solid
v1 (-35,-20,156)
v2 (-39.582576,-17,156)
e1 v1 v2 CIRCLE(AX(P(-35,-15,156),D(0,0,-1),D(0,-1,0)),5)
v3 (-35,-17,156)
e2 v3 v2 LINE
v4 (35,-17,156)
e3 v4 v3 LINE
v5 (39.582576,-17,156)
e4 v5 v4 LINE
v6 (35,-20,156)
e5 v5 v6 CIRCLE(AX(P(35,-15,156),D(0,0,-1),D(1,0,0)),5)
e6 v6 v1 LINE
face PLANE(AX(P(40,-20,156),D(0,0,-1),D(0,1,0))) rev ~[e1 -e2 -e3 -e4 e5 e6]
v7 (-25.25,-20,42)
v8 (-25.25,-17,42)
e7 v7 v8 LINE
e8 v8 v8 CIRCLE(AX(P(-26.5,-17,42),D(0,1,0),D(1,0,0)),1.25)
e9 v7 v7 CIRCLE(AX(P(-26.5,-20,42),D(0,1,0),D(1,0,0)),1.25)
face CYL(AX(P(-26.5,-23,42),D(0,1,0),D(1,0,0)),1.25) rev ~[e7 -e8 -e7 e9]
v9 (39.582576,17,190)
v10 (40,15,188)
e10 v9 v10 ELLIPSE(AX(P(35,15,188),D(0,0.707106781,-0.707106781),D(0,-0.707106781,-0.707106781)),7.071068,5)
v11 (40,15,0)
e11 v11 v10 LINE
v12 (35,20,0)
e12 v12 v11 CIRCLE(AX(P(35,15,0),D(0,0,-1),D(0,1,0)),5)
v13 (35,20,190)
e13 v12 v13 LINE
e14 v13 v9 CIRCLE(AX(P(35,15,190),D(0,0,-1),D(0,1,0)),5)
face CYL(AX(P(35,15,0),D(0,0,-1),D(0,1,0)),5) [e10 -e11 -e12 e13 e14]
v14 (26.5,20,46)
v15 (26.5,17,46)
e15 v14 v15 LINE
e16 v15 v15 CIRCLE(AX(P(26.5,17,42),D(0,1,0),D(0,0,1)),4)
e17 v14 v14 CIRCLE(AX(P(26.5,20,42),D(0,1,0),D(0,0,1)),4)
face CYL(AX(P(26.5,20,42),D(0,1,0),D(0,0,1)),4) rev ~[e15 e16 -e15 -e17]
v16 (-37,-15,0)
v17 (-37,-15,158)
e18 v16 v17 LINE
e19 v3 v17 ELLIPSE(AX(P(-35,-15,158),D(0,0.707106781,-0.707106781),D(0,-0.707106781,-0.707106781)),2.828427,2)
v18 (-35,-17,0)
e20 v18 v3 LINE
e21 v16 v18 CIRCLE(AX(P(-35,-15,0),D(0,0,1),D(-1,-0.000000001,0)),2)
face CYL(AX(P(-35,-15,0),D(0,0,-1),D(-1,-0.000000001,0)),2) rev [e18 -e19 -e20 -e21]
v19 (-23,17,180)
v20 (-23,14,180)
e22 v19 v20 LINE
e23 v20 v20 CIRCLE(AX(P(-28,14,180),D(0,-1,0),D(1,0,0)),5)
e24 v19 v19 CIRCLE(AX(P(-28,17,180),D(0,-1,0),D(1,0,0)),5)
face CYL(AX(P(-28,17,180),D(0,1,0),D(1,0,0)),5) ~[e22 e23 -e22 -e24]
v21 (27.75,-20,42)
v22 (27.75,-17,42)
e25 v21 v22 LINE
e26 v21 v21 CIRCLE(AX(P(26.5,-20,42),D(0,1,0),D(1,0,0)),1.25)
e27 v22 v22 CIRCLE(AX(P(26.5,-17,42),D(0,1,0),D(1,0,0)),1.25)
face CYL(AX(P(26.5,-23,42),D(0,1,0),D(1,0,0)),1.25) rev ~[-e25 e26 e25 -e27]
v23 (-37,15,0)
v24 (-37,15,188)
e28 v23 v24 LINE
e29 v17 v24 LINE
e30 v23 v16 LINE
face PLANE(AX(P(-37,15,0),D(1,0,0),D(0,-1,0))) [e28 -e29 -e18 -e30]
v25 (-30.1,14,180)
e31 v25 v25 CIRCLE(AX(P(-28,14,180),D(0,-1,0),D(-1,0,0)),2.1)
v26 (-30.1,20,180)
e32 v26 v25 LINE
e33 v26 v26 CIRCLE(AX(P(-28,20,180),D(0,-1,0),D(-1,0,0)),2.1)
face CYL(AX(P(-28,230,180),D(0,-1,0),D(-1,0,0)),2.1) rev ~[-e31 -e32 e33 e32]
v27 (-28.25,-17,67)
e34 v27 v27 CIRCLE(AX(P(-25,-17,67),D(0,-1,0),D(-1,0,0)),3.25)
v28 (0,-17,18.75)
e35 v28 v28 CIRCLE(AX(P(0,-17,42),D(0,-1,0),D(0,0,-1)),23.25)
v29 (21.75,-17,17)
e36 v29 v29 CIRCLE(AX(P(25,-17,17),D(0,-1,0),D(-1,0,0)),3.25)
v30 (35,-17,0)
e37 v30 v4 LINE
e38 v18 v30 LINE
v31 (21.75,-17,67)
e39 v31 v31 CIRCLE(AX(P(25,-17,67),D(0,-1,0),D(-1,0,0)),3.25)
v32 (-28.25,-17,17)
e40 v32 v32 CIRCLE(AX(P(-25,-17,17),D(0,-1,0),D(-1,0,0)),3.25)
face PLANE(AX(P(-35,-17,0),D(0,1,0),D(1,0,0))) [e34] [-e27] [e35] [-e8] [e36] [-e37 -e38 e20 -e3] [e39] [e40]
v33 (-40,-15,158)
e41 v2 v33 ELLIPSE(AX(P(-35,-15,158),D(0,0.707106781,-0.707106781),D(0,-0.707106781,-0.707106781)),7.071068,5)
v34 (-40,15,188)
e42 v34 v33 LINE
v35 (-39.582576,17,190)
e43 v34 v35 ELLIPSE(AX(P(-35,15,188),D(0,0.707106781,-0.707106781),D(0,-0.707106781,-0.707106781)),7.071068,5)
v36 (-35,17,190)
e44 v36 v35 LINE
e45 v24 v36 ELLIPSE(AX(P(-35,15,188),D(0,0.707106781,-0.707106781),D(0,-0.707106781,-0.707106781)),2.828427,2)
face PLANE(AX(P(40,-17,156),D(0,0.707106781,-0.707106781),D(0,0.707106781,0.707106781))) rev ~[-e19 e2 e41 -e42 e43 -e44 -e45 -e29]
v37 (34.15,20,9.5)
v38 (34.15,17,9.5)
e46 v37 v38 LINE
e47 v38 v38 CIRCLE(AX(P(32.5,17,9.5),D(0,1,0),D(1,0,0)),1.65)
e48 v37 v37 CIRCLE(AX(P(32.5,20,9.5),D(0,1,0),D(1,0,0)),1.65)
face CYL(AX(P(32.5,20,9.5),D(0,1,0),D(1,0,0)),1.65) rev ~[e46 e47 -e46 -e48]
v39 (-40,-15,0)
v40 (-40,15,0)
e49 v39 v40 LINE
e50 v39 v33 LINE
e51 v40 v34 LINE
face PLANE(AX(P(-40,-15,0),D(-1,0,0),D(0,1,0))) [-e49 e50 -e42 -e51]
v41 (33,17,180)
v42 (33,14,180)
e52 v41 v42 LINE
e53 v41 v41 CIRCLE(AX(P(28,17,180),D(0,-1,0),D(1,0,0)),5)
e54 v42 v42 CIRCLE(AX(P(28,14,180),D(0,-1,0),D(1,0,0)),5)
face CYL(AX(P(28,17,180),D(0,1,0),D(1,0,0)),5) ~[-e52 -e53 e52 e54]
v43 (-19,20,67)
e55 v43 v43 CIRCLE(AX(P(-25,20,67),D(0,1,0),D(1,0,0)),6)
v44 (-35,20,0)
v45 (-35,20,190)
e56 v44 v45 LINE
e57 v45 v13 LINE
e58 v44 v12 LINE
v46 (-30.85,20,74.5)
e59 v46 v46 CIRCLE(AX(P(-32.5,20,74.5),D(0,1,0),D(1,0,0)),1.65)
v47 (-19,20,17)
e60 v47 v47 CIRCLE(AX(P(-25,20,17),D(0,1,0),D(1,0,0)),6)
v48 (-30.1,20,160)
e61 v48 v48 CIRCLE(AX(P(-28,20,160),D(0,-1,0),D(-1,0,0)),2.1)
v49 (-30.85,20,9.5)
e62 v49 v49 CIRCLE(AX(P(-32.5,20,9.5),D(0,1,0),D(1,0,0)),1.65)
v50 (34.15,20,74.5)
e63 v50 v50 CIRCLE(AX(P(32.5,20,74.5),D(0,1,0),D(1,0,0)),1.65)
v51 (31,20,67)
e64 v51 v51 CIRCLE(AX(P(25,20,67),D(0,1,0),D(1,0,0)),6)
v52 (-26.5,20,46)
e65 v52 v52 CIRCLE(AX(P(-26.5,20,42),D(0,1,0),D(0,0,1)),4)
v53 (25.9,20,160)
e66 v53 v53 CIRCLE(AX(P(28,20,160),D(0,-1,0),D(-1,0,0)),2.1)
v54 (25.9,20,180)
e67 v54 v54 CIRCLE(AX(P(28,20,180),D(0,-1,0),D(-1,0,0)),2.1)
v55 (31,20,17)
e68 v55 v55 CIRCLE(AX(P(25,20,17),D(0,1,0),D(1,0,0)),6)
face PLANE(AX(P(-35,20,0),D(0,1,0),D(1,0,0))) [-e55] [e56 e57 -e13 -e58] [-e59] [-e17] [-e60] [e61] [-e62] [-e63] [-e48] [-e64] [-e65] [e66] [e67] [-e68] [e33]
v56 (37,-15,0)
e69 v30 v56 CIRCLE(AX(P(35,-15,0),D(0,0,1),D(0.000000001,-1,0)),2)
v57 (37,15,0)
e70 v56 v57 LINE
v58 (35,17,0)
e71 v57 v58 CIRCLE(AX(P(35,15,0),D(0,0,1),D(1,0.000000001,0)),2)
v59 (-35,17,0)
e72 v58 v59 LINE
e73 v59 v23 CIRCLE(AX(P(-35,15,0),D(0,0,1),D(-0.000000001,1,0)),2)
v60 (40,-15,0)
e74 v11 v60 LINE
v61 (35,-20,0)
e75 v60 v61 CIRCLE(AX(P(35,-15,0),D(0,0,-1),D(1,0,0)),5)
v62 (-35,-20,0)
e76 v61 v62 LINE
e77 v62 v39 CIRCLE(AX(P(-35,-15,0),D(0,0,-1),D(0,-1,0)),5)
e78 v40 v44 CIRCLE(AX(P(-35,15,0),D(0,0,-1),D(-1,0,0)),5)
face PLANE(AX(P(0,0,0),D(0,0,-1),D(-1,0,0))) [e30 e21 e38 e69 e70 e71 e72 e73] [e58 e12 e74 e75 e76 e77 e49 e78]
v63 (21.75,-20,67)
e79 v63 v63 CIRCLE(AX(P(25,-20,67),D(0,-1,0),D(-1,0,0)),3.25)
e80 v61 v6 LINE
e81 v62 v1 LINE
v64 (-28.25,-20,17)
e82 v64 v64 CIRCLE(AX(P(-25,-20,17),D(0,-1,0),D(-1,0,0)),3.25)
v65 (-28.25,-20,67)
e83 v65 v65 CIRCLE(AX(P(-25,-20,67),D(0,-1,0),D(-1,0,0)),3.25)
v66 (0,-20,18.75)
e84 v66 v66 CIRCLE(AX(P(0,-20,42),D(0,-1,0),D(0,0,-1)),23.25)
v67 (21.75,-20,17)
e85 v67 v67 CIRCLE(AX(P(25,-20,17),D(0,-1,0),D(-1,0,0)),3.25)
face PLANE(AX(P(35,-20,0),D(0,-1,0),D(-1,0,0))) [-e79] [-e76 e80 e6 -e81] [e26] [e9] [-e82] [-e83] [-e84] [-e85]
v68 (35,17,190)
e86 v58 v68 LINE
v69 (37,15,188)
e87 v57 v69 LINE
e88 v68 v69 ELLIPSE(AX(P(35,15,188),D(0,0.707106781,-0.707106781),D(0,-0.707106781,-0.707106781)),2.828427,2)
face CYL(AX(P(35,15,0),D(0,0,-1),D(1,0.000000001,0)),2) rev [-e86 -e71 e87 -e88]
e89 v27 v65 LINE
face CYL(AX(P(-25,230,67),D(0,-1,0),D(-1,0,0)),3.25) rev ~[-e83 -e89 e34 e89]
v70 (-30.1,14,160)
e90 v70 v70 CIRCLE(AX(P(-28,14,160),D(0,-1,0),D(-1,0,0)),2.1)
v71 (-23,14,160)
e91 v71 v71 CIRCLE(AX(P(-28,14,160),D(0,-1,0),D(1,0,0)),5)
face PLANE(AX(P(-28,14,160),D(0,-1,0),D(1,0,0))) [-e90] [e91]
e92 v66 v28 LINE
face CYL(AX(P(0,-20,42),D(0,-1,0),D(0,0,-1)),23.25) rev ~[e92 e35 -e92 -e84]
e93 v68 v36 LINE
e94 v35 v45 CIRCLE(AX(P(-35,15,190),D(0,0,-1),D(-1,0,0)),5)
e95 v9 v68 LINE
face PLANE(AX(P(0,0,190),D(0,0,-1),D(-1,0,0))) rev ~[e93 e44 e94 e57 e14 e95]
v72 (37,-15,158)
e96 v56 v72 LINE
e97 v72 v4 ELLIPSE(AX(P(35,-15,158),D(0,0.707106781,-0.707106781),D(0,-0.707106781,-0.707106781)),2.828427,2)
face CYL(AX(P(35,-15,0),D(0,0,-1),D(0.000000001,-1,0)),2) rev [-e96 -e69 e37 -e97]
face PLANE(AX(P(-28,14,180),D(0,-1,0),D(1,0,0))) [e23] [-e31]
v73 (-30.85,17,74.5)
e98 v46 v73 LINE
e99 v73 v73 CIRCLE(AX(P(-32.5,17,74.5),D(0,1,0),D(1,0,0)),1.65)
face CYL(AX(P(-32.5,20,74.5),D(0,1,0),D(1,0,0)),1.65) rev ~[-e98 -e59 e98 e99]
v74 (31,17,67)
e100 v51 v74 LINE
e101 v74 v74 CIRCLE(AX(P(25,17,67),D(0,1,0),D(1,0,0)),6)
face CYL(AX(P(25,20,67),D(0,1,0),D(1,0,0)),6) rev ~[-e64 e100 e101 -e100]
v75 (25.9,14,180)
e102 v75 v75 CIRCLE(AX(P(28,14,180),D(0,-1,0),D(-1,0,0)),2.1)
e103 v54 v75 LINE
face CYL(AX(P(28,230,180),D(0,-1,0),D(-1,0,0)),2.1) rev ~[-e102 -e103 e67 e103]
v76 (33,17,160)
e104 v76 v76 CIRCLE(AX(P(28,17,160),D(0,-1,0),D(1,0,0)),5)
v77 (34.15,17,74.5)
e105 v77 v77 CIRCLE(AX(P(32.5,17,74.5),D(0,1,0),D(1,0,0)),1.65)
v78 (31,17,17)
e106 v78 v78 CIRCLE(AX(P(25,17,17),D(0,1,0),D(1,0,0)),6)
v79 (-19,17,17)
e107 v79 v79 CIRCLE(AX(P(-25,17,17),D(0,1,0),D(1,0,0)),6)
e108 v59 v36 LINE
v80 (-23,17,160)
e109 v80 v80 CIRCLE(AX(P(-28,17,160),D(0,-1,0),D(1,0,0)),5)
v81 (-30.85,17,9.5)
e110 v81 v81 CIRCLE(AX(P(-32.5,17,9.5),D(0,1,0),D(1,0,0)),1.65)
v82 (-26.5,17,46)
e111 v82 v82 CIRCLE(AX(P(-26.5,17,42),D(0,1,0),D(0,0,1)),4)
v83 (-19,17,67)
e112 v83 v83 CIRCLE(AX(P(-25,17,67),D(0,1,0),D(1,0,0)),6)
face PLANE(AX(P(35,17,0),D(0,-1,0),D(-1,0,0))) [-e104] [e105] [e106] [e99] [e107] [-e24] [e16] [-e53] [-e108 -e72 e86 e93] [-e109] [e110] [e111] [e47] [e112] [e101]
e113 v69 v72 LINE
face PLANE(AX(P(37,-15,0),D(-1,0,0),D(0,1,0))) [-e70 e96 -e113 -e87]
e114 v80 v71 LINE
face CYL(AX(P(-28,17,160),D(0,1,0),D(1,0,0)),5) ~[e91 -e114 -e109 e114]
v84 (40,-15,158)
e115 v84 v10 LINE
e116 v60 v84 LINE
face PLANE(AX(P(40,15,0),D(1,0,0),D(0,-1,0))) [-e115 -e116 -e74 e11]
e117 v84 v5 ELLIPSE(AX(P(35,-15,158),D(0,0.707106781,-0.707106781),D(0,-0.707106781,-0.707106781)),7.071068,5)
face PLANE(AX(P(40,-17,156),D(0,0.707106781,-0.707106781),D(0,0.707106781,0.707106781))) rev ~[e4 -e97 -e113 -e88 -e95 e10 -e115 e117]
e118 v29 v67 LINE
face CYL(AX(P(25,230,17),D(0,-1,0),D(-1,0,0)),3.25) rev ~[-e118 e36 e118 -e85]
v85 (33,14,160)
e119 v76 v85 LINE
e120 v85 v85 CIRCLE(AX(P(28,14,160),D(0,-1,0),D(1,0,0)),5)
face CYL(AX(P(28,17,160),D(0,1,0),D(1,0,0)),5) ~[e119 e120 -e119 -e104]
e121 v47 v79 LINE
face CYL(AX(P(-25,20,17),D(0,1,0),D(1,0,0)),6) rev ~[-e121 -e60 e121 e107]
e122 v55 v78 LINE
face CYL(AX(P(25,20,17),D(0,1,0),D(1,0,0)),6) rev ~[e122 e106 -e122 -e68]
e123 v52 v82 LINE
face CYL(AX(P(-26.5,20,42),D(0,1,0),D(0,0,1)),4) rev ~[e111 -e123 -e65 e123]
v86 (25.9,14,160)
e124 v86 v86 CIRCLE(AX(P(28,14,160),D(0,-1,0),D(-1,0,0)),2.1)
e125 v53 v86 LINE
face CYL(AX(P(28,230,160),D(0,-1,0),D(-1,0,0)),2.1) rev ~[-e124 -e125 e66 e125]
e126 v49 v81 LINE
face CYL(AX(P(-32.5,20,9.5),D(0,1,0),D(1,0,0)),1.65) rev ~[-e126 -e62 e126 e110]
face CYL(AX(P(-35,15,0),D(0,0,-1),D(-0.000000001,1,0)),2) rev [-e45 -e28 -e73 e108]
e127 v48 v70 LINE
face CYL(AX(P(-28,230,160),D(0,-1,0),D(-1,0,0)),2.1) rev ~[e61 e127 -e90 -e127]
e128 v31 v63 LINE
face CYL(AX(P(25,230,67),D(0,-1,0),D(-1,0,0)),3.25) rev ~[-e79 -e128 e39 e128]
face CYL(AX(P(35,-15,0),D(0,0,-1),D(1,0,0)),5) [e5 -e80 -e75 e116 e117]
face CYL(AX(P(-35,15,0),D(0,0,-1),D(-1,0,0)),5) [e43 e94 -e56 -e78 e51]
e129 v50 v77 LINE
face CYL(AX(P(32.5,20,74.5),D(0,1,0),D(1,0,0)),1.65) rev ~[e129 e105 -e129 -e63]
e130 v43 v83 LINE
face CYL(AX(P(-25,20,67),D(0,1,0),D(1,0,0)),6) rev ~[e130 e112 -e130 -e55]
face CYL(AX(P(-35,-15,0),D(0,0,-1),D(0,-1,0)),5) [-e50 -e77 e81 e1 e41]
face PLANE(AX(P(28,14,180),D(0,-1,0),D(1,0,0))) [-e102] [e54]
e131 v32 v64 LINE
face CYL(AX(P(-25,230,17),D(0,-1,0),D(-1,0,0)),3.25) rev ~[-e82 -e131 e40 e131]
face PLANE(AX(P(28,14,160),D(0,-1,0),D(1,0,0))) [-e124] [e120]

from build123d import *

# Parameters (mm, degrees)
EXTRUDE_1_DEPTH              = 190
SKETCH_6_R                   = 23.25
CUT_EXTRUDE_1_DEPTH          = 3
HOLE_WIZARD_6_5_6_5_1_D      = 6.5
HOLE_WIZARD_12_0_12_1_REACH  = 200.242
HOLE_WIZARD_12_0_12_1_BORE_R = 6
HOLE_WIZARD_M4_1_REACH       = 200.242
HOLE_WIZARD_M4_1_BORE_R      = 1.65
CUT_EXTRUDE_2_DEPTH          = 208.123151772
SKETCH_12_R                  = 5
EXTRUDE_2_DEPTH              = 3
HOLE_WIZARD_M5_1_D           = 4.2
HOLE_WIZARD_M3_1_D           = 2.5
HOLE_WIZARD_M3_1_DEPTH       = 3
CUT_EXTRUDE_3_REACH          = 200.242
SKETCH_17_R                  = 4


with BuildPart() as part:
    # 草图1 → 凸台-拉伸1 (new body)
    with BuildSketch(Plane.XY):
        with BuildLine():
            Line((-35, 20), (35, 20))
            ThreePointArc((35, 20), (38.535533906, 18.535533906), (40, 15))
            Line((40, 15), (40, -15))
            ThreePointArc((40, -15), (38.535533906, -18.535533906), (35, -20))
            Line((35, -20), (-35, -20))
            ThreePointArc((-35, -20), (-38.535533906, -18.535533906), (-40, -15))
            Line((-40, -15), (-40, 15))
            ThreePointArc((-40, 15), (-38.535533906, 18.535533906), (-35, 20))
        make_face()
        with BuildLine():
            Line((-37, 15), (-37, -15))
            ThreePointArc((-37, -15), (-36.414213562, -16.414213562), (-35, -17))
            Line((-35, -17), (35, -17))
            ThreePointArc((35, -17), (36.414213562, -16.414213562), (37, -15))
            Line((37, -15), (37, 15))
            ThreePointArc((37, 15), (36.414213562, 16.414213562), (35, 17))
            Line((35, 17), (-35, 17))
            ThreePointArc((-35, 17), (-36.414213562, 16.414213562), (-37, 15))
        make_face(mode=Mode.SUBTRACT)
    extrude(amount=EXTRUDE_1_DEPTH)

    # 草图6 → 切除-拉伸1 (cut)
    with BuildSketch(Plane.XZ.offset(20)):
        with Locations(Location((0, 42, 0), (0, 0, 270))):
            Circle(SKETCH_6_R)
    extrude(amount=-CUT_EXTRUDE_1_DEPTH, mode=Mode.SUBTRACT)

    # Ø6.5 (6.5) 直径孔1 (through all)
    with Locations(Plane(origin=(0, 20, 0), x_dir=(1, 0, 0), z_dir=(0, 1, 0))):
        with Locations((-25, -17), (25, -17), (25, -67), (-25, -67)):
            Hole(HOLE_WIZARD_6_5_6_5_1_D / 2)

    # Ø12.0 (12) 直径孔1 bore → Ø12.0 (12) 直径孔1 (cut, up to next)
    with BuildSketch(Plane(origin=(0, 20, 0), x_dir=(1, 0, 0), z_dir=(0, 1, 0)), mode=Mode.PRIVATE) as hole_wizard_12_0_12_1_sk1:
        with Locations((-25, -17)):
            Circle(HOLE_WIZARD_12_0_12_1_BORE_R)
    hole_wizard_12_0_12_1_tool1 = extrude(hole_wizard_12_0_12_1_sk1.sketch, amount=-HOLE_WIZARD_12_0_12_1_REACH, mode=Mode.PRIVATE) & part.part
    # Ø12.0 (12) 直径孔1 bore → Ø12.0 (12) 直径孔1 (cut, up to next)
    with BuildSketch(Plane(origin=(0, 20, 0), x_dir=(1, 0, 0), z_dir=(0, 1, 0)), mode=Mode.PRIVATE) as hole_wizard_12_0_12_1_sk2:
        with Locations((25, -17)):
            Circle(HOLE_WIZARD_12_0_12_1_BORE_R)
    hole_wizard_12_0_12_1_tool2 = extrude(hole_wizard_12_0_12_1_sk2.sketch, amount=-HOLE_WIZARD_12_0_12_1_REACH, mode=Mode.PRIVATE) & part.part
    # Ø12.0 (12) 直径孔1 bore → Ø12.0 (12) 直径孔1 (cut, up to next)
    with BuildSketch(Plane(origin=(0, 20, 0), x_dir=(1, 0, 0), z_dir=(0, 1, 0)), mode=Mode.PRIVATE) as hole_wizard_12_0_12_1_sk3:
        with Locations((25, -67)):
            Circle(HOLE_WIZARD_12_0_12_1_BORE_R)
    hole_wizard_12_0_12_1_tool3 = extrude(hole_wizard_12_0_12_1_sk3.sketch, amount=-HOLE_WIZARD_12_0_12_1_REACH, mode=Mode.PRIVATE) & part.part
    # Ø12.0 (12) 直径孔1 bore → Ø12.0 (12) 直径孔1 (cut, up to next)
    with BuildSketch(Plane(origin=(0, 20, 0), x_dir=(1, 0, 0), z_dir=(0, 1, 0)), mode=Mode.PRIVATE) as hole_wizard_12_0_12_1_sk4:
        with Locations((-25, -67)):
            Circle(HOLE_WIZARD_12_0_12_1_BORE_R)
    hole_wizard_12_0_12_1_tool4 = extrude(hole_wizard_12_0_12_1_sk4.sketch, amount=-HOLE_WIZARD_12_0_12_1_REACH, mode=Mode.PRIVATE) & part.part
    add(hole_wizard_12_0_12_1_tool1.solids().sort_by_distance((-25, 20, 17))[0], mode=Mode.SUBTRACT)
    add(hole_wizard_12_0_12_1_tool2.solids().sort_by_distance((25, 20, 17))[0], mode=Mode.SUBTRACT)
    add(hole_wizard_12_0_12_1_tool3.solids().sort_by_distance((25, 20, 67))[0], mode=Mode.SUBTRACT)
    add(hole_wizard_12_0_12_1_tool4.solids().sort_by_distance((-25, 20, 67))[0], mode=Mode.SUBTRACT)

    # M4 螺纹孔1 bore → M4 螺纹孔1 (cut, up to next)
    with BuildSketch(Plane(origin=(0, 20, 0), x_dir=(1, 0, 0), z_dir=(0, 1, 0)), mode=Mode.PRIVATE) as hole_wizard_m4_1_sk1:
        with Locations((-32.5, -9.5)):
            Circle(HOLE_WIZARD_M4_1_BORE_R)
    hole_wizard_m4_1_tool1 = extrude(hole_wizard_m4_1_sk1.sketch, amount=-HOLE_WIZARD_M4_1_REACH, mode=Mode.PRIVATE) & part.part
    # M4 螺纹孔1 bore → M4 螺纹孔1 (cut, up to next)
    with BuildSketch(Plane(origin=(0, 20, 0), x_dir=(1, 0, 0), z_dir=(0, 1, 0)), mode=Mode.PRIVATE) as hole_wizard_m4_1_sk2:
        with Locations((32.5, -9.5)):
            Circle(HOLE_WIZARD_M4_1_BORE_R)
    hole_wizard_m4_1_tool2 = extrude(hole_wizard_m4_1_sk2.sketch, amount=-HOLE_WIZARD_M4_1_REACH, mode=Mode.PRIVATE) & part.part
    # M4 螺纹孔1 bore → M4 螺纹孔1 (cut, up to next)
    with BuildSketch(Plane(origin=(0, 20, 0), x_dir=(1, 0, 0), z_dir=(0, 1, 0)), mode=Mode.PRIVATE) as hole_wizard_m4_1_sk3:
        with Locations((32.5, -74.5)):
            Circle(HOLE_WIZARD_M4_1_BORE_R)
    hole_wizard_m4_1_tool3 = extrude(hole_wizard_m4_1_sk3.sketch, amount=-HOLE_WIZARD_M4_1_REACH, mode=Mode.PRIVATE) & part.part
    # M4 螺纹孔1 bore → M4 螺纹孔1 (cut, up to next)
    with BuildSketch(Plane(origin=(0, 20, 0), x_dir=(1, 0, 0), z_dir=(0, 1, 0)), mode=Mode.PRIVATE) as hole_wizard_m4_1_sk4:
        with Locations((-32.5, -74.5)):
            Circle(HOLE_WIZARD_M4_1_BORE_R)
    hole_wizard_m4_1_tool4 = extrude(hole_wizard_m4_1_sk4.sketch, amount=-HOLE_WIZARD_M4_1_REACH, mode=Mode.PRIVATE) & part.part
    add(hole_wizard_m4_1_tool1.solids().sort_by_distance((-32.5, 20, 9.5))[0], mode=Mode.SUBTRACT)
    add(hole_wizard_m4_1_tool2.solids().sort_by_distance((32.5, 20, 9.5))[0], mode=Mode.SUBTRACT)
    add(hole_wizard_m4_1_tool3.solids().sort_by_distance((32.5, 20, 74.5))[0], mode=Mode.SUBTRACT)
    add(hole_wizard_m4_1_tool4.solids().sort_by_distance((-32.5, 20, 74.5))[0], mode=Mode.SUBTRACT)

    # 草图9 → 切除-拉伸2 (cut, through all)
    with BuildSketch(Plane(origin=(40, 0, 0), x_dir=(0, 0, -1), z_dir=(1, 0, 0))):
        Polygon((-190, 17), (-190, -20), (-156, -20), (-156, -17), align=None)
    extrude(amount=-CUT_EXTRUDE_2_DEPTH, mode=Mode.SUBTRACT)

    # 草图12 → 凸台-拉伸2 (add)
    with BuildSketch(Plane.XZ.offset(-17)):
        with Locations((-28, 160)):
            Circle(SKETCH_12_R)
        with Locations((-28, 180)):
            Circle(SKETCH_12_R)
        with Locations((28, 160)):
            Circle(SKETCH_12_R)
        with Locations((28, 180)):
            Circle(SKETCH_12_R)
    extrude(amount=EXTRUDE_2_DEPTH)

    # M5 螺纹孔1 (through all)
    with Locations(Plane(origin=(0, 20, 0), x_dir=(1, 0, 0), z_dir=(0, 1, 0))):
        with Locations((-28, -160), (-28, -180), (28, -160), (28, -180)):
            Hole(HOLE_WIZARD_M5_1_D / 2)

    # M3 螺纹孔1
    with Locations(Plane(origin=(0, -20, 0), x_dir=(-1, 0, 0), z_dir=(0, -1, 0))):
        with Locations((26.5, -42), (-26.5, -42)):
            Hole(HOLE_WIZARD_M3_1_D / 2, depth=HOLE_WIZARD_M3_1_DEPTH)

    # 草图17 → 切除-拉伸3 (cut, up to next)
    with BuildSketch(Plane(origin=(0, 20, 0), x_dir=(1, 0, 0), z_dir=(0, 1, 0)), mode=Mode.PRIVATE) as cut_extrude_3_sk1:
        with Locations(Location((-26.5, -42, 0), (0, 0, 270))):
            Circle(SKETCH_17_R)
    cut_extrude_3_tool1 = extrude(cut_extrude_3_sk1.sketch, amount=-CUT_EXTRUDE_3_REACH, mode=Mode.PRIVATE) & part.part
    # 草图17 → 切除-拉伸3 (cut, up to next)
    with BuildSketch(Plane(origin=(0, 20, 0), x_dir=(1, 0, 0), z_dir=(0, 1, 0)), mode=Mode.PRIVATE) as cut_extrude_3_sk2:
        with Locations(Location((26.5, -42, 0), (0, 0, 270))):
            Circle(SKETCH_17_R)
    cut_extrude_3_tool2 = extrude(cut_extrude_3_sk2.sketch, amount=-CUT_EXTRUDE_3_REACH, mode=Mode.PRIVATE) & part.part
    add(cut_extrude_3_tool1.solids().sort_by_distance((-26.5, 20, 42))[0], mode=Mode.SUBTRACT)
    add(cut_extrude_3_tool2.solids().sort_by_distance((26.5, 20, 42))[0], mode=Mode.SUBTRACT)


solid = part.part
